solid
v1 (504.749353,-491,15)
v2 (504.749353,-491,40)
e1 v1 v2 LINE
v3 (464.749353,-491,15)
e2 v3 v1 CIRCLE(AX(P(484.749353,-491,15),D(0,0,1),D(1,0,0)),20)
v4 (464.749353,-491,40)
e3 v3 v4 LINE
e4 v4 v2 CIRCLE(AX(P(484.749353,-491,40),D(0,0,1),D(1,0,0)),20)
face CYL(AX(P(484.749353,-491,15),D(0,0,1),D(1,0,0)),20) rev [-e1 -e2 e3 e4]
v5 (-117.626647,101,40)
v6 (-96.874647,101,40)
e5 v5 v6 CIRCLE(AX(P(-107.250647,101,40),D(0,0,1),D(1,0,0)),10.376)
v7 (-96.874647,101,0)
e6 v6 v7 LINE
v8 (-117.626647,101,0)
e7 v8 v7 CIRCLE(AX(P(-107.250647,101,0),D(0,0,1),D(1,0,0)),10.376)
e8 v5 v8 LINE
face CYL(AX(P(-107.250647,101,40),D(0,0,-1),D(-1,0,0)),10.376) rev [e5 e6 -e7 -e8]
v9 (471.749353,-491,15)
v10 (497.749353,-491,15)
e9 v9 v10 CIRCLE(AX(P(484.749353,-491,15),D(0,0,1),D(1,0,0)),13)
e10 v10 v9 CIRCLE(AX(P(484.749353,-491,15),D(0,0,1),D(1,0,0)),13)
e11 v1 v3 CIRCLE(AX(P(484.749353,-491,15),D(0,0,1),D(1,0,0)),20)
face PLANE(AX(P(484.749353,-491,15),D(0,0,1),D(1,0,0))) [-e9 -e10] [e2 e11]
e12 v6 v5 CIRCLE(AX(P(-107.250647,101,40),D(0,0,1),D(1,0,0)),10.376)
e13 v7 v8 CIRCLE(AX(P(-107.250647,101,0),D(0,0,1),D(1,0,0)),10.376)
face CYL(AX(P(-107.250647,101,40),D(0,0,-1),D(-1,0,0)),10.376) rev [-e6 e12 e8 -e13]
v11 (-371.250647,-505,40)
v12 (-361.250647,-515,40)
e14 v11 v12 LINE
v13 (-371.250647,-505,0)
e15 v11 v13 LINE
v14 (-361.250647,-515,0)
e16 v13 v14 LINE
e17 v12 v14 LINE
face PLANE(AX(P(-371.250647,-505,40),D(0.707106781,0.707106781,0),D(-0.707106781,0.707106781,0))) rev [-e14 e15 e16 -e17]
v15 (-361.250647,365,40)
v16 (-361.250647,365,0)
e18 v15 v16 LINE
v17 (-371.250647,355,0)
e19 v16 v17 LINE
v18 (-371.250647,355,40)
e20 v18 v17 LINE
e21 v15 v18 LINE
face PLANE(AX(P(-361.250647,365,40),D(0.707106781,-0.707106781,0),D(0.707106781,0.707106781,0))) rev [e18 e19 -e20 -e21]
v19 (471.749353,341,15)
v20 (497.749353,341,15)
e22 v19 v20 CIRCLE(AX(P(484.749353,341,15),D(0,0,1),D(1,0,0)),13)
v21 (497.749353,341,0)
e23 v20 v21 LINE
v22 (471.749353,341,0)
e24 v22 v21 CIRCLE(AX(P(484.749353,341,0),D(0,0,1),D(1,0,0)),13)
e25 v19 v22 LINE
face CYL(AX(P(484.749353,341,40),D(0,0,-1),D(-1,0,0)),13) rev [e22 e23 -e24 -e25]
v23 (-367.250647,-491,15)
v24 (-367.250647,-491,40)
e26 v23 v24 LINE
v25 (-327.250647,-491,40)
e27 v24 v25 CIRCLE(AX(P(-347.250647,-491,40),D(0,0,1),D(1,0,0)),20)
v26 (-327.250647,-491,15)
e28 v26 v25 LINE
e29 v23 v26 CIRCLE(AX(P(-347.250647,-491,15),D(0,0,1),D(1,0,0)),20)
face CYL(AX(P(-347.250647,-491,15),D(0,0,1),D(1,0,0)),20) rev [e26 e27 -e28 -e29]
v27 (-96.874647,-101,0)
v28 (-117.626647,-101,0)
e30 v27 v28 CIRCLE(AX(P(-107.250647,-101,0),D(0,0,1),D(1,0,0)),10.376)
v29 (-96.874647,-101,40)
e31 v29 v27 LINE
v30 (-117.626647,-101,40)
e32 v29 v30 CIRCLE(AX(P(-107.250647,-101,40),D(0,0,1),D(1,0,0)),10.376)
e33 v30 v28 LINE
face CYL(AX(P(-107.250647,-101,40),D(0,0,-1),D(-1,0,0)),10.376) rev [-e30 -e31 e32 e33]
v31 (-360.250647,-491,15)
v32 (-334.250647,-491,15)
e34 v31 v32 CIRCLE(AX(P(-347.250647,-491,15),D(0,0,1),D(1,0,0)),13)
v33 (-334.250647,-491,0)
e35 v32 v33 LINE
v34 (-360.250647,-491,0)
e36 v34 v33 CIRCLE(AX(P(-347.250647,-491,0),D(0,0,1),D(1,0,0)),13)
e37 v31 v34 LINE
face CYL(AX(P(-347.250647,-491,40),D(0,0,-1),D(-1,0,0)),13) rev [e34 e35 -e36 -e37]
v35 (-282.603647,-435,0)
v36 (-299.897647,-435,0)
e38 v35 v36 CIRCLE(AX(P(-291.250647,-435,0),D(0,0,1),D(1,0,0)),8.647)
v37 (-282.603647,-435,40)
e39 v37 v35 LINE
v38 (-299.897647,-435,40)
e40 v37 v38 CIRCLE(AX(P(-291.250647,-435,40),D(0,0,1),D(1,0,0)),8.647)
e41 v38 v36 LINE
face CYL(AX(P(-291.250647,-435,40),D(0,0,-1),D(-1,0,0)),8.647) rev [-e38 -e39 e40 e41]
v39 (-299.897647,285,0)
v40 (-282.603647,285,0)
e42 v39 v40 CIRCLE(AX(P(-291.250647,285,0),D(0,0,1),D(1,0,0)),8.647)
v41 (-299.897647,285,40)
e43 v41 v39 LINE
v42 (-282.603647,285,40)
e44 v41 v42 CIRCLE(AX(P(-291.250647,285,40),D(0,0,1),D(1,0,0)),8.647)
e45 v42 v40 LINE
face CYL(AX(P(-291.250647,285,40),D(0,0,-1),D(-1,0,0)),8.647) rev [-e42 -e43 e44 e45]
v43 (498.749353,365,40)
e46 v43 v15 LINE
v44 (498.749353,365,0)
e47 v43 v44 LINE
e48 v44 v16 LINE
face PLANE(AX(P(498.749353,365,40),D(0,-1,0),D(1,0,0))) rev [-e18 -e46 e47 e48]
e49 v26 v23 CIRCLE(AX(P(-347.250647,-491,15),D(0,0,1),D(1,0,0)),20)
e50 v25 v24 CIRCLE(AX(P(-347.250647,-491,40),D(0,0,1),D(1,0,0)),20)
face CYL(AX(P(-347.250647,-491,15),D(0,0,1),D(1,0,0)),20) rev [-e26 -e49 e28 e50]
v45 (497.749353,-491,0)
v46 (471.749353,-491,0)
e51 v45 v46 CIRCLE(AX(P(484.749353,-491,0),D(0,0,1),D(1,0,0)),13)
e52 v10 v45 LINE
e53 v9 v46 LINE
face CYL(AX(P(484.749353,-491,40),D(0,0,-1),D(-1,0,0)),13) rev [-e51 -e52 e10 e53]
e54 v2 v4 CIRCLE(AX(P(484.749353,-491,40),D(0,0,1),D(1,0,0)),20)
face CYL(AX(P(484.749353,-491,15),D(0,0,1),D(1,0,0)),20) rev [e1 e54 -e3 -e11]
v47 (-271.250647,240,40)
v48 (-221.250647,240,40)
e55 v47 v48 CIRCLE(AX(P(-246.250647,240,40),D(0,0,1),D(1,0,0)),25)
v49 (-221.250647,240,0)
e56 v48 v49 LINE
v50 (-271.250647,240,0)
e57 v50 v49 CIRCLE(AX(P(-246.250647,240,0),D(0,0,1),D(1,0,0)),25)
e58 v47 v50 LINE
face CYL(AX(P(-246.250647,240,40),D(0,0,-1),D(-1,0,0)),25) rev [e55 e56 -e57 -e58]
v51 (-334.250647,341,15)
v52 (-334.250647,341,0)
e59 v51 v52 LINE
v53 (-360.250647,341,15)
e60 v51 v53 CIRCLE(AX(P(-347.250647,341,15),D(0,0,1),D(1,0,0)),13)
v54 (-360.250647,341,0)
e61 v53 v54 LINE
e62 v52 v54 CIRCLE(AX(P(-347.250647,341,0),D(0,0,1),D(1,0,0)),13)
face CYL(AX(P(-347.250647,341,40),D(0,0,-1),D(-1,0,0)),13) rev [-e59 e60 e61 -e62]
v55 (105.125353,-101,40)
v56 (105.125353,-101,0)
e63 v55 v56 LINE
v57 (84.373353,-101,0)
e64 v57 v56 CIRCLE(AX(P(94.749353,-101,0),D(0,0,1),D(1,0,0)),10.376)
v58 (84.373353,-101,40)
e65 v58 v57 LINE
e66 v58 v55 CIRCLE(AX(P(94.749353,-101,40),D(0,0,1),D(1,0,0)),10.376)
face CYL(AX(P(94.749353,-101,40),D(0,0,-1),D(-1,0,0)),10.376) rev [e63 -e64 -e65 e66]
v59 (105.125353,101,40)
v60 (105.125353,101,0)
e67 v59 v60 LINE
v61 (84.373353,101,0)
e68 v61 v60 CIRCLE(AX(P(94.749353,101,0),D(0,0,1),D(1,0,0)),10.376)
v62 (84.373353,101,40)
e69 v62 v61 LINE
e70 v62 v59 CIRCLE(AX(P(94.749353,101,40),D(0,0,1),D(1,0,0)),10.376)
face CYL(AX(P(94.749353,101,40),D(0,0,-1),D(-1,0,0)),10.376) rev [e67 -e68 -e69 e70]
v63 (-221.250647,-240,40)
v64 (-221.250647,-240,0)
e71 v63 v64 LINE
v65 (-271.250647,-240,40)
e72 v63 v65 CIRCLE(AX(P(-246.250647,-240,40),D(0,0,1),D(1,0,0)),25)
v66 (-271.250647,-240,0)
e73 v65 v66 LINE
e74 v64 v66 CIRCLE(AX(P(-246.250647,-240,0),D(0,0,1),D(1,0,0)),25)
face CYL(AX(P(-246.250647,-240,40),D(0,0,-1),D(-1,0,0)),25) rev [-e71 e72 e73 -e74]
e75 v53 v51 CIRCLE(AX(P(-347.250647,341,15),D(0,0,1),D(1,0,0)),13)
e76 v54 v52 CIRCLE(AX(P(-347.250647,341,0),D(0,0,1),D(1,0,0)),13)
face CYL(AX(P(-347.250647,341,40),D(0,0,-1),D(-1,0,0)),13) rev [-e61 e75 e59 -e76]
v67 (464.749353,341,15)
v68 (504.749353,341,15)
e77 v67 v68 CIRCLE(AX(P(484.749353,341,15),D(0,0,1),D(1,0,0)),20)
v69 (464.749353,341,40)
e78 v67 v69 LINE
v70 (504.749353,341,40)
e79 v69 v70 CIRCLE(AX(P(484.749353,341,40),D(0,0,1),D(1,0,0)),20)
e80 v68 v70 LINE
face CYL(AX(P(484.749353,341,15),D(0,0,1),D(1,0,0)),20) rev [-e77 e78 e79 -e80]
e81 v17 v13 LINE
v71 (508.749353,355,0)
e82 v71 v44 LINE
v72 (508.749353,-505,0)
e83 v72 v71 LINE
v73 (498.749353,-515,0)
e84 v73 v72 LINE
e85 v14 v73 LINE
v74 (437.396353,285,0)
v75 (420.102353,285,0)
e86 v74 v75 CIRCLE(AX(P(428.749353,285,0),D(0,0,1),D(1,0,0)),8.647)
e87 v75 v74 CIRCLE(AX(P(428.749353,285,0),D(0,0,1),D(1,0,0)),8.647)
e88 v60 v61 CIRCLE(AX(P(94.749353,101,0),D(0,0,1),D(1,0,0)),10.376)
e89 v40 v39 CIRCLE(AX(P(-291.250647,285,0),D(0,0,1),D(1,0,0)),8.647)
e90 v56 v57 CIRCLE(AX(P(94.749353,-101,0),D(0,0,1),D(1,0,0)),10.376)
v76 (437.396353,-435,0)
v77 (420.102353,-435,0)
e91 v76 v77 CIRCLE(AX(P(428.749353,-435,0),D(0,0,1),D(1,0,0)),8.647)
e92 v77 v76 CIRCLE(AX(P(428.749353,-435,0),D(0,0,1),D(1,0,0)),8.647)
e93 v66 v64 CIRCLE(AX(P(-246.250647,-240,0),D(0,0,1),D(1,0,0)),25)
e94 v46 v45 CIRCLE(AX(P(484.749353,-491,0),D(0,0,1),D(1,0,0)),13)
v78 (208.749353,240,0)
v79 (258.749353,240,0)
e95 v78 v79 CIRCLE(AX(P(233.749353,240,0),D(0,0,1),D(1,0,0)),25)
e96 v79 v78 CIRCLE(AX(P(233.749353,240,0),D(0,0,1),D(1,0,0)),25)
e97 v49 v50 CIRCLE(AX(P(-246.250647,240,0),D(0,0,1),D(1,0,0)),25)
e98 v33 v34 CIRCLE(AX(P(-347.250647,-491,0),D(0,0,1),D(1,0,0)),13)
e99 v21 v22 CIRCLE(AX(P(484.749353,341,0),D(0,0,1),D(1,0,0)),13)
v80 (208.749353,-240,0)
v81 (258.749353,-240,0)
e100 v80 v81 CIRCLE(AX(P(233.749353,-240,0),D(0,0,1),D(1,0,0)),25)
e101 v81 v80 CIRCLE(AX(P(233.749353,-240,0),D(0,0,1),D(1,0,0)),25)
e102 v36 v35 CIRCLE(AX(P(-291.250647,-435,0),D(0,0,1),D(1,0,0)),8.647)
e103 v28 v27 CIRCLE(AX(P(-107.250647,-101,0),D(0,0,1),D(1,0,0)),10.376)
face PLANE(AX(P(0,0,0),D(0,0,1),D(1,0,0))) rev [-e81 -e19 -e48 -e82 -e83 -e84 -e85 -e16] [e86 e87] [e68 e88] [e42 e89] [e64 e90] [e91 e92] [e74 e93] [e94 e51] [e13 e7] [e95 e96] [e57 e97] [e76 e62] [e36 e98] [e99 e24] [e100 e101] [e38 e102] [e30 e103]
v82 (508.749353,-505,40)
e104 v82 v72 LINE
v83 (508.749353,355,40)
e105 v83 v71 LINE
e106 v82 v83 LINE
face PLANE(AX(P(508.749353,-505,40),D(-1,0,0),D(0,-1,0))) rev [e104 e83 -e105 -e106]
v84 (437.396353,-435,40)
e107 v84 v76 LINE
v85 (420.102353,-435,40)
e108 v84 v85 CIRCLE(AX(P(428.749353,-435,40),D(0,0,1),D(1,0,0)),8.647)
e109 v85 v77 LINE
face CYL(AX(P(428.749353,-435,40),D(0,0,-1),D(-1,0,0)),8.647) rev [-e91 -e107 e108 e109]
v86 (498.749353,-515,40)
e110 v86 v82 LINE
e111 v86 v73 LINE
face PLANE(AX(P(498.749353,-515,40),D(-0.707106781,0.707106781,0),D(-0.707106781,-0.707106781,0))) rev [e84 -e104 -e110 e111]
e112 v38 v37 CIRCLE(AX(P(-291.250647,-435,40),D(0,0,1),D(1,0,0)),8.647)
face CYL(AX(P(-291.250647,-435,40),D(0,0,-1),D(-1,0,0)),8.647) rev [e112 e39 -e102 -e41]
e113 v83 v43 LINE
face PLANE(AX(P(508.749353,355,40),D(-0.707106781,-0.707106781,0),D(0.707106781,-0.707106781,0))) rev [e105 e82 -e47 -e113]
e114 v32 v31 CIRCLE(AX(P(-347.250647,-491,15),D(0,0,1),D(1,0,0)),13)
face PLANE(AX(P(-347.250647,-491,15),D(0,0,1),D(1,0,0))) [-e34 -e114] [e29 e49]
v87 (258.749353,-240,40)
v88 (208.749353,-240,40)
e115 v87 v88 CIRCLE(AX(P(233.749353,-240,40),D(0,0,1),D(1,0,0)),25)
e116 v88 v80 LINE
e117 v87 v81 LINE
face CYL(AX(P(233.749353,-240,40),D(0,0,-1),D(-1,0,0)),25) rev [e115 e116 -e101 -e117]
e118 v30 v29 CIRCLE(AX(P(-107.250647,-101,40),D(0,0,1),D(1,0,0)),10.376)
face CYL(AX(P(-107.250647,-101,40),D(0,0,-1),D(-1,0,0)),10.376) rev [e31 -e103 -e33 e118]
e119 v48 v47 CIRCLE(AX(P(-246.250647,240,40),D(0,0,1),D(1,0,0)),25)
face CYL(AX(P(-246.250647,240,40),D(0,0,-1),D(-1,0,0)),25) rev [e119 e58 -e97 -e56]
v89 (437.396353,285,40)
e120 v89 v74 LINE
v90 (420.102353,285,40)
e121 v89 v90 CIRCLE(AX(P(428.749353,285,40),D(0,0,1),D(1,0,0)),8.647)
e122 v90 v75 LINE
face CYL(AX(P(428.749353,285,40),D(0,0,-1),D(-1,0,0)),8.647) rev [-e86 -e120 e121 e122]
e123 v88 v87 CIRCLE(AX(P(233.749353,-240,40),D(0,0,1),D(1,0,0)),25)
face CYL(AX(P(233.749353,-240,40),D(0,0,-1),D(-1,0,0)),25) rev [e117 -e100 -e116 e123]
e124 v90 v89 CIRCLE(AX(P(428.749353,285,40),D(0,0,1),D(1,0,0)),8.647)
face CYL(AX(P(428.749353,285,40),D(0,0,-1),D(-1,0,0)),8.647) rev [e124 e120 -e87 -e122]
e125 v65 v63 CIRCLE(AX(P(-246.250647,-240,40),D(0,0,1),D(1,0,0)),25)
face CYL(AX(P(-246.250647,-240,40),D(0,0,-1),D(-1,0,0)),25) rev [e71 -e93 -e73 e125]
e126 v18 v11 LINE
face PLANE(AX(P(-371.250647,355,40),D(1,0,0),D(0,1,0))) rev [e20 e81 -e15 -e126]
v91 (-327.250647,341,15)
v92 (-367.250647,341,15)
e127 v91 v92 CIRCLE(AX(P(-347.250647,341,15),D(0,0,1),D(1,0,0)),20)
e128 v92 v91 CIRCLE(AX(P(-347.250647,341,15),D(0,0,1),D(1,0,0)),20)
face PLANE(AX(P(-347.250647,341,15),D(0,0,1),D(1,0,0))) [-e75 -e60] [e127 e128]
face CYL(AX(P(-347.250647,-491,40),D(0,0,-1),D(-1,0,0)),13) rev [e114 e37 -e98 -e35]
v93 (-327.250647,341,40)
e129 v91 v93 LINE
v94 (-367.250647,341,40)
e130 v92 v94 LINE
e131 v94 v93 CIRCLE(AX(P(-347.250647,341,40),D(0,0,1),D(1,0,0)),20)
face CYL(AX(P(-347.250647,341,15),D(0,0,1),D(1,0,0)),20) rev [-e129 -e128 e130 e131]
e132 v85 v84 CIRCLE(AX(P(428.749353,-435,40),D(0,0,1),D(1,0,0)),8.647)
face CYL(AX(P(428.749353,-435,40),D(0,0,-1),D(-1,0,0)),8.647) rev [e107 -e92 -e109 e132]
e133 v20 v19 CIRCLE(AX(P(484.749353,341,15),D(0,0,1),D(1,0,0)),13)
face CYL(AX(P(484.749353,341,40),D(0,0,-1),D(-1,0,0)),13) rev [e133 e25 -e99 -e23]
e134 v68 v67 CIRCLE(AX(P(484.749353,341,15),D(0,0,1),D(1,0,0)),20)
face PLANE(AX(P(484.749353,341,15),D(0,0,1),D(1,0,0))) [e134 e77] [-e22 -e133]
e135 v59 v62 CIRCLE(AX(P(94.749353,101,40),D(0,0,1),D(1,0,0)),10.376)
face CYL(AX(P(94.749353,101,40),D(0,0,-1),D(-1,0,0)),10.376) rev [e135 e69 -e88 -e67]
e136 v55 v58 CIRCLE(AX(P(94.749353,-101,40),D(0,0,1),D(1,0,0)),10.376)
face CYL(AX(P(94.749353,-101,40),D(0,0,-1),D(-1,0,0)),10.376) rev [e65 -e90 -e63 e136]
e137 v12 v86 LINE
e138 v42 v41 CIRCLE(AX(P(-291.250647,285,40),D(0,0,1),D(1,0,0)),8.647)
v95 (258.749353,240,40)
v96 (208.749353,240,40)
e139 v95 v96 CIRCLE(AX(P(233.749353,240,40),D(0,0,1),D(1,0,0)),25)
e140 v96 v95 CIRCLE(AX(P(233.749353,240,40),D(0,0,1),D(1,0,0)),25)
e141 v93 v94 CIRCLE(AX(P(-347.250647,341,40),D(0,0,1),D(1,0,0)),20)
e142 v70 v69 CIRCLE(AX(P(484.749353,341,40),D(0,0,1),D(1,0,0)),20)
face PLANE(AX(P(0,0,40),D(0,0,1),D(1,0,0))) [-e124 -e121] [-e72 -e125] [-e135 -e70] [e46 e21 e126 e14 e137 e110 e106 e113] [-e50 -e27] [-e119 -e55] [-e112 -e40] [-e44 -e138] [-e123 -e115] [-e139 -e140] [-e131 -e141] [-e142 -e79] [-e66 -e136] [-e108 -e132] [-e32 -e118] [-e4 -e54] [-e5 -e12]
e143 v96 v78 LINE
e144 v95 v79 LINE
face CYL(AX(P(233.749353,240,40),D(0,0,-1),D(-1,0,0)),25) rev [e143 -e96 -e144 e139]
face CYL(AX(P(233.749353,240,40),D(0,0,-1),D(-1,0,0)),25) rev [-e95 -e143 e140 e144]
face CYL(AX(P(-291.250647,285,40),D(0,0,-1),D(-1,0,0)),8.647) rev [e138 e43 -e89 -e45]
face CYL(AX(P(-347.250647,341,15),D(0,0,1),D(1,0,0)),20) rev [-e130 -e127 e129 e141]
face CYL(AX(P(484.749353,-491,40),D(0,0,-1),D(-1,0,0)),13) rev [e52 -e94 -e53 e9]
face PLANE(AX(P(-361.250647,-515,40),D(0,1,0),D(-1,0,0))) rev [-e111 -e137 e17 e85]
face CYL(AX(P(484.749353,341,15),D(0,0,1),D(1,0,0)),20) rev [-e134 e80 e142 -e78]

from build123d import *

# Parameters (mm, degrees)
SKETCH1_R           = 8.647
SKETCH1_R_2         = 13
SKETCH1_R_3         = 10.376
SKETCH1_R_4         = 25
BOSS_EXTRUDE1_DEPTH = 40
SKETCH2_R           = 20
CUT_EXTRUDE1_DEPTH  = 25


with BuildPart() as part:
    # Sketch1 → Boss-Extrude1 (new body)
    with BuildSketch(Plane.XY):
        Polygon((498.749353033, 365), (-361.250646967, 365), (-371.250646967, 355), (-371.250646967, -505), (-361.250646967, -515), (498.749353033, -515), (508.749353033, -505), (508.749353033, 355), align=None)
        with Locations((428.749353033, -435)):
            Circle(SKETCH1_R, mode=Mode.SUBTRACT)
        with Locations((-291.250646967, 285)):
            Circle(SKETCH1_R, mode=Mode.SUBTRACT)
        with Locations((428.749353033, 285)):
            Circle(SKETCH1_R, mode=Mode.SUBTRACT)
        with Locations((-291.250646967, -435)):
            Circle(SKETCH1_R, mode=Mode.SUBTRACT)
        with Locations((484.749353033, -491)):
            Circle(SKETCH1_R_2, mode=Mode.SUBTRACT)
        with Locations((-347.250646967, 341)):
            Circle(SKETCH1_R_2, mode=Mode.SUBTRACT)
        with Locations((484.749353033, 341)):
            Circle(SKETCH1_R_2, mode=Mode.SUBTRACT)
        with Locations((-347.250646967, -491)):
            Circle(SKETCH1_R_2, mode=Mode.SUBTRACT)
        with Locations((-107.250646967, -101)):
            Circle(SKETCH1_R_3, mode=Mode.SUBTRACT)
        with Locations((94.749353033, 101)):
            Circle(SKETCH1_R_3, mode=Mode.SUBTRACT)
        with Locations((-107.250646967, 101)):
            Circle(SKETCH1_R_3, mode=Mode.SUBTRACT)
        with Locations((94.749353033, -101)):
            Circle(SKETCH1_R_3, mode=Mode.SUBTRACT)
        with Locations((-246.250646967, -240)):
            Circle(SKETCH1_R_4, mode=Mode.SUBTRACT)
        with Locations((233.749353033, 240)):
            Circle(SKETCH1_R_4, mode=Mode.SUBTRACT)
        with Locations((-246.250646967, 240)):
            Circle(SKETCH1_R_4, mode=Mode.SUBTRACT)
        with Locations((233.749353033, -240)):
            Circle(SKETCH1_R_4, mode=Mode.SUBTRACT)
    extrude(amount=BOSS_EXTRUDE1_DEPTH)

    # Sketch2 → Cut-Extrude1 (cut)
    with BuildSketch(Plane.XY.offset(40)):
        with Locations((-347.250646967, 341)):
            Circle(SKETCH2_R)
        with Locations((484.749353033, 341)):
            Circle(SKETCH2_R)
        with Locations((484.749353033, -491)):
            Circle(SKETCH2_R)
        with Locations((-347.250646967, -491)):
            Circle(SKETCH2_R)
    extrude(amount=-CUT_EXTRUDE1_DEPTH, mode=Mode.SUBTRACT)


solid = part.part
